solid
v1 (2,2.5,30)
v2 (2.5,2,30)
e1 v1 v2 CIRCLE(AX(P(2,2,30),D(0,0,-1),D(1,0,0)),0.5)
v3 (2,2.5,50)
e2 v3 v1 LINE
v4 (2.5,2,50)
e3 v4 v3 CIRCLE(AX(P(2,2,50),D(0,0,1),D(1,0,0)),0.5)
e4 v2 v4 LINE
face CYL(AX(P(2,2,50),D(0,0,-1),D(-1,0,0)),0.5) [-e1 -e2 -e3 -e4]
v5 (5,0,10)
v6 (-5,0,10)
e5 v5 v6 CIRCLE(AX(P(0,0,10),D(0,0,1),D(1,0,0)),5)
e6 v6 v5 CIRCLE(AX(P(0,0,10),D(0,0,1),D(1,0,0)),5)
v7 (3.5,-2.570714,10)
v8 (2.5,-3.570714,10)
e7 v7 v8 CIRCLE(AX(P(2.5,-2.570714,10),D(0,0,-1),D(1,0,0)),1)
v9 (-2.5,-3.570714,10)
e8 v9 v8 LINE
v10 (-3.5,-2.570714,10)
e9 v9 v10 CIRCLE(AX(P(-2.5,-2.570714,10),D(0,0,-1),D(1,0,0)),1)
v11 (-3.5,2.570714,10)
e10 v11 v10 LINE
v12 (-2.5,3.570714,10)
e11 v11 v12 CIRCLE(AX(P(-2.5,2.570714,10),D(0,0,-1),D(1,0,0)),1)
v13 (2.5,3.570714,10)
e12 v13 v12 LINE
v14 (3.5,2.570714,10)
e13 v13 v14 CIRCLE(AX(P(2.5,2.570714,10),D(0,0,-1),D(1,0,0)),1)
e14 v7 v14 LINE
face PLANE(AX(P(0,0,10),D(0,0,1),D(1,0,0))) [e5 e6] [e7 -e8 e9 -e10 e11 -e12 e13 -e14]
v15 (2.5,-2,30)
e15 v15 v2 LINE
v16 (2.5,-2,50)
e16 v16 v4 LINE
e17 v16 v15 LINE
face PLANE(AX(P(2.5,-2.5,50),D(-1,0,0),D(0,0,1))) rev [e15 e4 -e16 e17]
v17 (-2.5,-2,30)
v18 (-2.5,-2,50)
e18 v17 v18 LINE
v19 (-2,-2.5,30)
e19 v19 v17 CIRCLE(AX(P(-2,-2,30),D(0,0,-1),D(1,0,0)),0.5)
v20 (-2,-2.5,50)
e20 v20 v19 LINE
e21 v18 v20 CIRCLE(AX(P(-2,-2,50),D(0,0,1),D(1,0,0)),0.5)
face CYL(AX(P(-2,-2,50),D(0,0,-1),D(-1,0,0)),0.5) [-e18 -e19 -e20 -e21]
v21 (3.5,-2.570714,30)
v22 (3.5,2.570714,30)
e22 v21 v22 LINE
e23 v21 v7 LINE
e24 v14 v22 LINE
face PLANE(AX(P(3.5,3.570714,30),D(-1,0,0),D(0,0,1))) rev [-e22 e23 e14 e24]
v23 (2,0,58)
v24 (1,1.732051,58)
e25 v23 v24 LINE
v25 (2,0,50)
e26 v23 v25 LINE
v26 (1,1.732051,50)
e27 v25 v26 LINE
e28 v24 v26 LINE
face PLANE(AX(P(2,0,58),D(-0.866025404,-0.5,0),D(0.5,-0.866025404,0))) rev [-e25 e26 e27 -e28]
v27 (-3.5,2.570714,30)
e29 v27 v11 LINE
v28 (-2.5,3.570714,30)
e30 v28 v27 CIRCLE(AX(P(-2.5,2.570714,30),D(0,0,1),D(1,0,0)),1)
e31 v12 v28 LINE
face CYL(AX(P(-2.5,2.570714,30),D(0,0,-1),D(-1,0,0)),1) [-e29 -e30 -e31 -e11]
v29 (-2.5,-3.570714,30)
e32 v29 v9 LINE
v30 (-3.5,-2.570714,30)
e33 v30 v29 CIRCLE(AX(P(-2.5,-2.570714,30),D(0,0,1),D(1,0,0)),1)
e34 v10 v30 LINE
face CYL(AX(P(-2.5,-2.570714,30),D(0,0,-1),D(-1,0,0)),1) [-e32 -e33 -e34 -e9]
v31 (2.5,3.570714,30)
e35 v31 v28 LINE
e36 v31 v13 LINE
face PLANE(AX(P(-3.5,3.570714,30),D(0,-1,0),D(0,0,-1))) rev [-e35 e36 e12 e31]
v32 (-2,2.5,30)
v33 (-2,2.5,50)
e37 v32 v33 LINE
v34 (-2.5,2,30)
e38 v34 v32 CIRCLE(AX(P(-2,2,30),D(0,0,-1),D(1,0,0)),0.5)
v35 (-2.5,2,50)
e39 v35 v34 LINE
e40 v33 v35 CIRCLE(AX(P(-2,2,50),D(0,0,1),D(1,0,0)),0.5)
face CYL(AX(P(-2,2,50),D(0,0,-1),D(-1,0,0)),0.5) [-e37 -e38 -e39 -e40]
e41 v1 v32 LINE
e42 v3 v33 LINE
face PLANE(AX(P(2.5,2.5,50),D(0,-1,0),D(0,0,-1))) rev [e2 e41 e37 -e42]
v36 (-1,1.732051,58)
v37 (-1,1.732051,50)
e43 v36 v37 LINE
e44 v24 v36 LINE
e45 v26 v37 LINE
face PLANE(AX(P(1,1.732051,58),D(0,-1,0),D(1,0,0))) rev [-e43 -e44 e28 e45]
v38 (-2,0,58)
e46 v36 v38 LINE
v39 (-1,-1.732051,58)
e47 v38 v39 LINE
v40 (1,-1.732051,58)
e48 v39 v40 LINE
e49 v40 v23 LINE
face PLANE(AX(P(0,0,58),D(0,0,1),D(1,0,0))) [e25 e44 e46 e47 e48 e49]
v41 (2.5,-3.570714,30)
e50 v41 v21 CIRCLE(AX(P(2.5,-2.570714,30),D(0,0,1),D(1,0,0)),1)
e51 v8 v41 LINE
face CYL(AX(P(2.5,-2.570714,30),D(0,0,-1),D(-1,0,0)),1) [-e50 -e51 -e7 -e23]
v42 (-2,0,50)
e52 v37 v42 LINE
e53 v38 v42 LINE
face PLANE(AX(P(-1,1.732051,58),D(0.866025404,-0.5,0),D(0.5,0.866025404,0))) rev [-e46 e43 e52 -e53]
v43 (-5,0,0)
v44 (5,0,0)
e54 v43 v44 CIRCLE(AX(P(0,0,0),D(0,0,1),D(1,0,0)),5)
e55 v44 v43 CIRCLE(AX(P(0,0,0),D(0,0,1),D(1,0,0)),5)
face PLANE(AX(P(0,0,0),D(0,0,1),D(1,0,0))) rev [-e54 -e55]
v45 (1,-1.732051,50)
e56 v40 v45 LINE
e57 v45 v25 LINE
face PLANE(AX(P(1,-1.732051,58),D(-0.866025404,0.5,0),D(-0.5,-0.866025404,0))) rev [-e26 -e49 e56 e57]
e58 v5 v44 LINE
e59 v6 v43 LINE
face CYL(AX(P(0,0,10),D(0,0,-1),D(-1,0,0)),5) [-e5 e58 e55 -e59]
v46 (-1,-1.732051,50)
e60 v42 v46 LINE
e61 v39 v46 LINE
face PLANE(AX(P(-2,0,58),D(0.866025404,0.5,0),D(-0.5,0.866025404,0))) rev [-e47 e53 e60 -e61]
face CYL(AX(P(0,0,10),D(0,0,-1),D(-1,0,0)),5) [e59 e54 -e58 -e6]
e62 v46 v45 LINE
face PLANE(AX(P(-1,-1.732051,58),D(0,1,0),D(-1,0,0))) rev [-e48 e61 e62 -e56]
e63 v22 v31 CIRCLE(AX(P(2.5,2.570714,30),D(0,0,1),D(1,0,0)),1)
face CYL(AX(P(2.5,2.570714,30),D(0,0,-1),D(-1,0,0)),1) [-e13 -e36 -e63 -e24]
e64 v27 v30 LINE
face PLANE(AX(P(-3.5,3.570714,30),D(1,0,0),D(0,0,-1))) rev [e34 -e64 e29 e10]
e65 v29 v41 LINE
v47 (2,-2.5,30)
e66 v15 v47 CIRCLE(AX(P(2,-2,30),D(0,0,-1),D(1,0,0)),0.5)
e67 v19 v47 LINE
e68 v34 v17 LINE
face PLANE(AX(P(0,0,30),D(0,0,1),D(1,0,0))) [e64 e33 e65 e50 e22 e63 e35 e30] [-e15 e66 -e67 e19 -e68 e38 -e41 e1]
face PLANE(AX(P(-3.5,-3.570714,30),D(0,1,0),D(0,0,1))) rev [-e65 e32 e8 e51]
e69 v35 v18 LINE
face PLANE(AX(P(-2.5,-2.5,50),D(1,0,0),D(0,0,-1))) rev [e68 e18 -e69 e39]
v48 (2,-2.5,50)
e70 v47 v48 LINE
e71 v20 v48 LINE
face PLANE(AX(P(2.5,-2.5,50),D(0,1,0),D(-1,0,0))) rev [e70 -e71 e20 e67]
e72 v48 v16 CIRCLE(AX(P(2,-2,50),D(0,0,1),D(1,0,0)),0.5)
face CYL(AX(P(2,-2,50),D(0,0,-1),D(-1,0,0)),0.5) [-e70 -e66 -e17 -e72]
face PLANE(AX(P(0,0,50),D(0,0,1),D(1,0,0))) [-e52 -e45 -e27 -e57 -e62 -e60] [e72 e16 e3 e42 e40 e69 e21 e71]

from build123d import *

# Parameters (mm, degrees)
SKETCH1_R           = 5
BOSS_EXTRUDE1_DEPTH = 10
SKETCH2_W           = 7
SKETCH2_H           = 7.141428428
BOSS_EXTRUDE2_DEPTH = 20
FILLET1_R           = 1
SKETCH3_W           = 5
SKETCH3_H           = 5
BOSS_EXTRUDE3_DEPTH = 20
FILLET2_R           = 0.5
BOSS_EXTRUDE4_DEPTH = 8


with BuildPart() as part:
    # Sketch1 → Boss-Extrude1 (new body)
    with BuildSketch(Plane.XY):
        Circle(SKETCH1_R)
    extrude(amount=BOSS_EXTRUDE1_DEPTH)

    # Sketch2 → Boss-Extrude2 (add)
    with BuildSketch(Plane.XY.offset(10)):
        Rectangle(SKETCH2_W, SKETCH2_H)
    extrude(amount=BOSS_EXTRUDE2_DEPTH)

    # Fillet1
    fillet1_edges = [part.edges().sort_by_distance(p)[0] for p in [
        (3.5, -3.570714214, 20),
        (3.5, 3.570714214, 20),
        (-3.5, 3.570714214, 20),
        (-3.5, -3.570714214, 20),
    ]]
    fillet(fillet1_edges, radius=FILLET1_R)

    # Sketch3 → Boss-Extrude3 (add)
    with BuildSketch(Plane.XY.offset(30)):
        Rectangle(SKETCH3_W, SKETCH3_H)
    extrude(amount=BOSS_EXTRUDE3_DEPTH)

    # Fillet2
    fillet2_edges = [part.edges().sort_by_distance(p)[0] for p in [
        (-2.5, 2.5, 40),
        (-2.5, -2.5, 40),
        (2.5, -2.5, 40),
        (2.5, 2.5, 40),
    ]]
    fillet(fillet2_edges, radius=FILLET2_R)

    # Sketch4 → Boss-Extrude4 (add)
    with BuildSketch(Plane.XY.offset(50)):
        Polygon((1, 1.732050808), (-1, 1.732050808), (-2, 0), (-1, -1.732050808), (1, -1.732050808), (2, 0), align=None)
    extrude(amount=BOSS_EXTRUDE4_DEPTH)


solid = part.part
